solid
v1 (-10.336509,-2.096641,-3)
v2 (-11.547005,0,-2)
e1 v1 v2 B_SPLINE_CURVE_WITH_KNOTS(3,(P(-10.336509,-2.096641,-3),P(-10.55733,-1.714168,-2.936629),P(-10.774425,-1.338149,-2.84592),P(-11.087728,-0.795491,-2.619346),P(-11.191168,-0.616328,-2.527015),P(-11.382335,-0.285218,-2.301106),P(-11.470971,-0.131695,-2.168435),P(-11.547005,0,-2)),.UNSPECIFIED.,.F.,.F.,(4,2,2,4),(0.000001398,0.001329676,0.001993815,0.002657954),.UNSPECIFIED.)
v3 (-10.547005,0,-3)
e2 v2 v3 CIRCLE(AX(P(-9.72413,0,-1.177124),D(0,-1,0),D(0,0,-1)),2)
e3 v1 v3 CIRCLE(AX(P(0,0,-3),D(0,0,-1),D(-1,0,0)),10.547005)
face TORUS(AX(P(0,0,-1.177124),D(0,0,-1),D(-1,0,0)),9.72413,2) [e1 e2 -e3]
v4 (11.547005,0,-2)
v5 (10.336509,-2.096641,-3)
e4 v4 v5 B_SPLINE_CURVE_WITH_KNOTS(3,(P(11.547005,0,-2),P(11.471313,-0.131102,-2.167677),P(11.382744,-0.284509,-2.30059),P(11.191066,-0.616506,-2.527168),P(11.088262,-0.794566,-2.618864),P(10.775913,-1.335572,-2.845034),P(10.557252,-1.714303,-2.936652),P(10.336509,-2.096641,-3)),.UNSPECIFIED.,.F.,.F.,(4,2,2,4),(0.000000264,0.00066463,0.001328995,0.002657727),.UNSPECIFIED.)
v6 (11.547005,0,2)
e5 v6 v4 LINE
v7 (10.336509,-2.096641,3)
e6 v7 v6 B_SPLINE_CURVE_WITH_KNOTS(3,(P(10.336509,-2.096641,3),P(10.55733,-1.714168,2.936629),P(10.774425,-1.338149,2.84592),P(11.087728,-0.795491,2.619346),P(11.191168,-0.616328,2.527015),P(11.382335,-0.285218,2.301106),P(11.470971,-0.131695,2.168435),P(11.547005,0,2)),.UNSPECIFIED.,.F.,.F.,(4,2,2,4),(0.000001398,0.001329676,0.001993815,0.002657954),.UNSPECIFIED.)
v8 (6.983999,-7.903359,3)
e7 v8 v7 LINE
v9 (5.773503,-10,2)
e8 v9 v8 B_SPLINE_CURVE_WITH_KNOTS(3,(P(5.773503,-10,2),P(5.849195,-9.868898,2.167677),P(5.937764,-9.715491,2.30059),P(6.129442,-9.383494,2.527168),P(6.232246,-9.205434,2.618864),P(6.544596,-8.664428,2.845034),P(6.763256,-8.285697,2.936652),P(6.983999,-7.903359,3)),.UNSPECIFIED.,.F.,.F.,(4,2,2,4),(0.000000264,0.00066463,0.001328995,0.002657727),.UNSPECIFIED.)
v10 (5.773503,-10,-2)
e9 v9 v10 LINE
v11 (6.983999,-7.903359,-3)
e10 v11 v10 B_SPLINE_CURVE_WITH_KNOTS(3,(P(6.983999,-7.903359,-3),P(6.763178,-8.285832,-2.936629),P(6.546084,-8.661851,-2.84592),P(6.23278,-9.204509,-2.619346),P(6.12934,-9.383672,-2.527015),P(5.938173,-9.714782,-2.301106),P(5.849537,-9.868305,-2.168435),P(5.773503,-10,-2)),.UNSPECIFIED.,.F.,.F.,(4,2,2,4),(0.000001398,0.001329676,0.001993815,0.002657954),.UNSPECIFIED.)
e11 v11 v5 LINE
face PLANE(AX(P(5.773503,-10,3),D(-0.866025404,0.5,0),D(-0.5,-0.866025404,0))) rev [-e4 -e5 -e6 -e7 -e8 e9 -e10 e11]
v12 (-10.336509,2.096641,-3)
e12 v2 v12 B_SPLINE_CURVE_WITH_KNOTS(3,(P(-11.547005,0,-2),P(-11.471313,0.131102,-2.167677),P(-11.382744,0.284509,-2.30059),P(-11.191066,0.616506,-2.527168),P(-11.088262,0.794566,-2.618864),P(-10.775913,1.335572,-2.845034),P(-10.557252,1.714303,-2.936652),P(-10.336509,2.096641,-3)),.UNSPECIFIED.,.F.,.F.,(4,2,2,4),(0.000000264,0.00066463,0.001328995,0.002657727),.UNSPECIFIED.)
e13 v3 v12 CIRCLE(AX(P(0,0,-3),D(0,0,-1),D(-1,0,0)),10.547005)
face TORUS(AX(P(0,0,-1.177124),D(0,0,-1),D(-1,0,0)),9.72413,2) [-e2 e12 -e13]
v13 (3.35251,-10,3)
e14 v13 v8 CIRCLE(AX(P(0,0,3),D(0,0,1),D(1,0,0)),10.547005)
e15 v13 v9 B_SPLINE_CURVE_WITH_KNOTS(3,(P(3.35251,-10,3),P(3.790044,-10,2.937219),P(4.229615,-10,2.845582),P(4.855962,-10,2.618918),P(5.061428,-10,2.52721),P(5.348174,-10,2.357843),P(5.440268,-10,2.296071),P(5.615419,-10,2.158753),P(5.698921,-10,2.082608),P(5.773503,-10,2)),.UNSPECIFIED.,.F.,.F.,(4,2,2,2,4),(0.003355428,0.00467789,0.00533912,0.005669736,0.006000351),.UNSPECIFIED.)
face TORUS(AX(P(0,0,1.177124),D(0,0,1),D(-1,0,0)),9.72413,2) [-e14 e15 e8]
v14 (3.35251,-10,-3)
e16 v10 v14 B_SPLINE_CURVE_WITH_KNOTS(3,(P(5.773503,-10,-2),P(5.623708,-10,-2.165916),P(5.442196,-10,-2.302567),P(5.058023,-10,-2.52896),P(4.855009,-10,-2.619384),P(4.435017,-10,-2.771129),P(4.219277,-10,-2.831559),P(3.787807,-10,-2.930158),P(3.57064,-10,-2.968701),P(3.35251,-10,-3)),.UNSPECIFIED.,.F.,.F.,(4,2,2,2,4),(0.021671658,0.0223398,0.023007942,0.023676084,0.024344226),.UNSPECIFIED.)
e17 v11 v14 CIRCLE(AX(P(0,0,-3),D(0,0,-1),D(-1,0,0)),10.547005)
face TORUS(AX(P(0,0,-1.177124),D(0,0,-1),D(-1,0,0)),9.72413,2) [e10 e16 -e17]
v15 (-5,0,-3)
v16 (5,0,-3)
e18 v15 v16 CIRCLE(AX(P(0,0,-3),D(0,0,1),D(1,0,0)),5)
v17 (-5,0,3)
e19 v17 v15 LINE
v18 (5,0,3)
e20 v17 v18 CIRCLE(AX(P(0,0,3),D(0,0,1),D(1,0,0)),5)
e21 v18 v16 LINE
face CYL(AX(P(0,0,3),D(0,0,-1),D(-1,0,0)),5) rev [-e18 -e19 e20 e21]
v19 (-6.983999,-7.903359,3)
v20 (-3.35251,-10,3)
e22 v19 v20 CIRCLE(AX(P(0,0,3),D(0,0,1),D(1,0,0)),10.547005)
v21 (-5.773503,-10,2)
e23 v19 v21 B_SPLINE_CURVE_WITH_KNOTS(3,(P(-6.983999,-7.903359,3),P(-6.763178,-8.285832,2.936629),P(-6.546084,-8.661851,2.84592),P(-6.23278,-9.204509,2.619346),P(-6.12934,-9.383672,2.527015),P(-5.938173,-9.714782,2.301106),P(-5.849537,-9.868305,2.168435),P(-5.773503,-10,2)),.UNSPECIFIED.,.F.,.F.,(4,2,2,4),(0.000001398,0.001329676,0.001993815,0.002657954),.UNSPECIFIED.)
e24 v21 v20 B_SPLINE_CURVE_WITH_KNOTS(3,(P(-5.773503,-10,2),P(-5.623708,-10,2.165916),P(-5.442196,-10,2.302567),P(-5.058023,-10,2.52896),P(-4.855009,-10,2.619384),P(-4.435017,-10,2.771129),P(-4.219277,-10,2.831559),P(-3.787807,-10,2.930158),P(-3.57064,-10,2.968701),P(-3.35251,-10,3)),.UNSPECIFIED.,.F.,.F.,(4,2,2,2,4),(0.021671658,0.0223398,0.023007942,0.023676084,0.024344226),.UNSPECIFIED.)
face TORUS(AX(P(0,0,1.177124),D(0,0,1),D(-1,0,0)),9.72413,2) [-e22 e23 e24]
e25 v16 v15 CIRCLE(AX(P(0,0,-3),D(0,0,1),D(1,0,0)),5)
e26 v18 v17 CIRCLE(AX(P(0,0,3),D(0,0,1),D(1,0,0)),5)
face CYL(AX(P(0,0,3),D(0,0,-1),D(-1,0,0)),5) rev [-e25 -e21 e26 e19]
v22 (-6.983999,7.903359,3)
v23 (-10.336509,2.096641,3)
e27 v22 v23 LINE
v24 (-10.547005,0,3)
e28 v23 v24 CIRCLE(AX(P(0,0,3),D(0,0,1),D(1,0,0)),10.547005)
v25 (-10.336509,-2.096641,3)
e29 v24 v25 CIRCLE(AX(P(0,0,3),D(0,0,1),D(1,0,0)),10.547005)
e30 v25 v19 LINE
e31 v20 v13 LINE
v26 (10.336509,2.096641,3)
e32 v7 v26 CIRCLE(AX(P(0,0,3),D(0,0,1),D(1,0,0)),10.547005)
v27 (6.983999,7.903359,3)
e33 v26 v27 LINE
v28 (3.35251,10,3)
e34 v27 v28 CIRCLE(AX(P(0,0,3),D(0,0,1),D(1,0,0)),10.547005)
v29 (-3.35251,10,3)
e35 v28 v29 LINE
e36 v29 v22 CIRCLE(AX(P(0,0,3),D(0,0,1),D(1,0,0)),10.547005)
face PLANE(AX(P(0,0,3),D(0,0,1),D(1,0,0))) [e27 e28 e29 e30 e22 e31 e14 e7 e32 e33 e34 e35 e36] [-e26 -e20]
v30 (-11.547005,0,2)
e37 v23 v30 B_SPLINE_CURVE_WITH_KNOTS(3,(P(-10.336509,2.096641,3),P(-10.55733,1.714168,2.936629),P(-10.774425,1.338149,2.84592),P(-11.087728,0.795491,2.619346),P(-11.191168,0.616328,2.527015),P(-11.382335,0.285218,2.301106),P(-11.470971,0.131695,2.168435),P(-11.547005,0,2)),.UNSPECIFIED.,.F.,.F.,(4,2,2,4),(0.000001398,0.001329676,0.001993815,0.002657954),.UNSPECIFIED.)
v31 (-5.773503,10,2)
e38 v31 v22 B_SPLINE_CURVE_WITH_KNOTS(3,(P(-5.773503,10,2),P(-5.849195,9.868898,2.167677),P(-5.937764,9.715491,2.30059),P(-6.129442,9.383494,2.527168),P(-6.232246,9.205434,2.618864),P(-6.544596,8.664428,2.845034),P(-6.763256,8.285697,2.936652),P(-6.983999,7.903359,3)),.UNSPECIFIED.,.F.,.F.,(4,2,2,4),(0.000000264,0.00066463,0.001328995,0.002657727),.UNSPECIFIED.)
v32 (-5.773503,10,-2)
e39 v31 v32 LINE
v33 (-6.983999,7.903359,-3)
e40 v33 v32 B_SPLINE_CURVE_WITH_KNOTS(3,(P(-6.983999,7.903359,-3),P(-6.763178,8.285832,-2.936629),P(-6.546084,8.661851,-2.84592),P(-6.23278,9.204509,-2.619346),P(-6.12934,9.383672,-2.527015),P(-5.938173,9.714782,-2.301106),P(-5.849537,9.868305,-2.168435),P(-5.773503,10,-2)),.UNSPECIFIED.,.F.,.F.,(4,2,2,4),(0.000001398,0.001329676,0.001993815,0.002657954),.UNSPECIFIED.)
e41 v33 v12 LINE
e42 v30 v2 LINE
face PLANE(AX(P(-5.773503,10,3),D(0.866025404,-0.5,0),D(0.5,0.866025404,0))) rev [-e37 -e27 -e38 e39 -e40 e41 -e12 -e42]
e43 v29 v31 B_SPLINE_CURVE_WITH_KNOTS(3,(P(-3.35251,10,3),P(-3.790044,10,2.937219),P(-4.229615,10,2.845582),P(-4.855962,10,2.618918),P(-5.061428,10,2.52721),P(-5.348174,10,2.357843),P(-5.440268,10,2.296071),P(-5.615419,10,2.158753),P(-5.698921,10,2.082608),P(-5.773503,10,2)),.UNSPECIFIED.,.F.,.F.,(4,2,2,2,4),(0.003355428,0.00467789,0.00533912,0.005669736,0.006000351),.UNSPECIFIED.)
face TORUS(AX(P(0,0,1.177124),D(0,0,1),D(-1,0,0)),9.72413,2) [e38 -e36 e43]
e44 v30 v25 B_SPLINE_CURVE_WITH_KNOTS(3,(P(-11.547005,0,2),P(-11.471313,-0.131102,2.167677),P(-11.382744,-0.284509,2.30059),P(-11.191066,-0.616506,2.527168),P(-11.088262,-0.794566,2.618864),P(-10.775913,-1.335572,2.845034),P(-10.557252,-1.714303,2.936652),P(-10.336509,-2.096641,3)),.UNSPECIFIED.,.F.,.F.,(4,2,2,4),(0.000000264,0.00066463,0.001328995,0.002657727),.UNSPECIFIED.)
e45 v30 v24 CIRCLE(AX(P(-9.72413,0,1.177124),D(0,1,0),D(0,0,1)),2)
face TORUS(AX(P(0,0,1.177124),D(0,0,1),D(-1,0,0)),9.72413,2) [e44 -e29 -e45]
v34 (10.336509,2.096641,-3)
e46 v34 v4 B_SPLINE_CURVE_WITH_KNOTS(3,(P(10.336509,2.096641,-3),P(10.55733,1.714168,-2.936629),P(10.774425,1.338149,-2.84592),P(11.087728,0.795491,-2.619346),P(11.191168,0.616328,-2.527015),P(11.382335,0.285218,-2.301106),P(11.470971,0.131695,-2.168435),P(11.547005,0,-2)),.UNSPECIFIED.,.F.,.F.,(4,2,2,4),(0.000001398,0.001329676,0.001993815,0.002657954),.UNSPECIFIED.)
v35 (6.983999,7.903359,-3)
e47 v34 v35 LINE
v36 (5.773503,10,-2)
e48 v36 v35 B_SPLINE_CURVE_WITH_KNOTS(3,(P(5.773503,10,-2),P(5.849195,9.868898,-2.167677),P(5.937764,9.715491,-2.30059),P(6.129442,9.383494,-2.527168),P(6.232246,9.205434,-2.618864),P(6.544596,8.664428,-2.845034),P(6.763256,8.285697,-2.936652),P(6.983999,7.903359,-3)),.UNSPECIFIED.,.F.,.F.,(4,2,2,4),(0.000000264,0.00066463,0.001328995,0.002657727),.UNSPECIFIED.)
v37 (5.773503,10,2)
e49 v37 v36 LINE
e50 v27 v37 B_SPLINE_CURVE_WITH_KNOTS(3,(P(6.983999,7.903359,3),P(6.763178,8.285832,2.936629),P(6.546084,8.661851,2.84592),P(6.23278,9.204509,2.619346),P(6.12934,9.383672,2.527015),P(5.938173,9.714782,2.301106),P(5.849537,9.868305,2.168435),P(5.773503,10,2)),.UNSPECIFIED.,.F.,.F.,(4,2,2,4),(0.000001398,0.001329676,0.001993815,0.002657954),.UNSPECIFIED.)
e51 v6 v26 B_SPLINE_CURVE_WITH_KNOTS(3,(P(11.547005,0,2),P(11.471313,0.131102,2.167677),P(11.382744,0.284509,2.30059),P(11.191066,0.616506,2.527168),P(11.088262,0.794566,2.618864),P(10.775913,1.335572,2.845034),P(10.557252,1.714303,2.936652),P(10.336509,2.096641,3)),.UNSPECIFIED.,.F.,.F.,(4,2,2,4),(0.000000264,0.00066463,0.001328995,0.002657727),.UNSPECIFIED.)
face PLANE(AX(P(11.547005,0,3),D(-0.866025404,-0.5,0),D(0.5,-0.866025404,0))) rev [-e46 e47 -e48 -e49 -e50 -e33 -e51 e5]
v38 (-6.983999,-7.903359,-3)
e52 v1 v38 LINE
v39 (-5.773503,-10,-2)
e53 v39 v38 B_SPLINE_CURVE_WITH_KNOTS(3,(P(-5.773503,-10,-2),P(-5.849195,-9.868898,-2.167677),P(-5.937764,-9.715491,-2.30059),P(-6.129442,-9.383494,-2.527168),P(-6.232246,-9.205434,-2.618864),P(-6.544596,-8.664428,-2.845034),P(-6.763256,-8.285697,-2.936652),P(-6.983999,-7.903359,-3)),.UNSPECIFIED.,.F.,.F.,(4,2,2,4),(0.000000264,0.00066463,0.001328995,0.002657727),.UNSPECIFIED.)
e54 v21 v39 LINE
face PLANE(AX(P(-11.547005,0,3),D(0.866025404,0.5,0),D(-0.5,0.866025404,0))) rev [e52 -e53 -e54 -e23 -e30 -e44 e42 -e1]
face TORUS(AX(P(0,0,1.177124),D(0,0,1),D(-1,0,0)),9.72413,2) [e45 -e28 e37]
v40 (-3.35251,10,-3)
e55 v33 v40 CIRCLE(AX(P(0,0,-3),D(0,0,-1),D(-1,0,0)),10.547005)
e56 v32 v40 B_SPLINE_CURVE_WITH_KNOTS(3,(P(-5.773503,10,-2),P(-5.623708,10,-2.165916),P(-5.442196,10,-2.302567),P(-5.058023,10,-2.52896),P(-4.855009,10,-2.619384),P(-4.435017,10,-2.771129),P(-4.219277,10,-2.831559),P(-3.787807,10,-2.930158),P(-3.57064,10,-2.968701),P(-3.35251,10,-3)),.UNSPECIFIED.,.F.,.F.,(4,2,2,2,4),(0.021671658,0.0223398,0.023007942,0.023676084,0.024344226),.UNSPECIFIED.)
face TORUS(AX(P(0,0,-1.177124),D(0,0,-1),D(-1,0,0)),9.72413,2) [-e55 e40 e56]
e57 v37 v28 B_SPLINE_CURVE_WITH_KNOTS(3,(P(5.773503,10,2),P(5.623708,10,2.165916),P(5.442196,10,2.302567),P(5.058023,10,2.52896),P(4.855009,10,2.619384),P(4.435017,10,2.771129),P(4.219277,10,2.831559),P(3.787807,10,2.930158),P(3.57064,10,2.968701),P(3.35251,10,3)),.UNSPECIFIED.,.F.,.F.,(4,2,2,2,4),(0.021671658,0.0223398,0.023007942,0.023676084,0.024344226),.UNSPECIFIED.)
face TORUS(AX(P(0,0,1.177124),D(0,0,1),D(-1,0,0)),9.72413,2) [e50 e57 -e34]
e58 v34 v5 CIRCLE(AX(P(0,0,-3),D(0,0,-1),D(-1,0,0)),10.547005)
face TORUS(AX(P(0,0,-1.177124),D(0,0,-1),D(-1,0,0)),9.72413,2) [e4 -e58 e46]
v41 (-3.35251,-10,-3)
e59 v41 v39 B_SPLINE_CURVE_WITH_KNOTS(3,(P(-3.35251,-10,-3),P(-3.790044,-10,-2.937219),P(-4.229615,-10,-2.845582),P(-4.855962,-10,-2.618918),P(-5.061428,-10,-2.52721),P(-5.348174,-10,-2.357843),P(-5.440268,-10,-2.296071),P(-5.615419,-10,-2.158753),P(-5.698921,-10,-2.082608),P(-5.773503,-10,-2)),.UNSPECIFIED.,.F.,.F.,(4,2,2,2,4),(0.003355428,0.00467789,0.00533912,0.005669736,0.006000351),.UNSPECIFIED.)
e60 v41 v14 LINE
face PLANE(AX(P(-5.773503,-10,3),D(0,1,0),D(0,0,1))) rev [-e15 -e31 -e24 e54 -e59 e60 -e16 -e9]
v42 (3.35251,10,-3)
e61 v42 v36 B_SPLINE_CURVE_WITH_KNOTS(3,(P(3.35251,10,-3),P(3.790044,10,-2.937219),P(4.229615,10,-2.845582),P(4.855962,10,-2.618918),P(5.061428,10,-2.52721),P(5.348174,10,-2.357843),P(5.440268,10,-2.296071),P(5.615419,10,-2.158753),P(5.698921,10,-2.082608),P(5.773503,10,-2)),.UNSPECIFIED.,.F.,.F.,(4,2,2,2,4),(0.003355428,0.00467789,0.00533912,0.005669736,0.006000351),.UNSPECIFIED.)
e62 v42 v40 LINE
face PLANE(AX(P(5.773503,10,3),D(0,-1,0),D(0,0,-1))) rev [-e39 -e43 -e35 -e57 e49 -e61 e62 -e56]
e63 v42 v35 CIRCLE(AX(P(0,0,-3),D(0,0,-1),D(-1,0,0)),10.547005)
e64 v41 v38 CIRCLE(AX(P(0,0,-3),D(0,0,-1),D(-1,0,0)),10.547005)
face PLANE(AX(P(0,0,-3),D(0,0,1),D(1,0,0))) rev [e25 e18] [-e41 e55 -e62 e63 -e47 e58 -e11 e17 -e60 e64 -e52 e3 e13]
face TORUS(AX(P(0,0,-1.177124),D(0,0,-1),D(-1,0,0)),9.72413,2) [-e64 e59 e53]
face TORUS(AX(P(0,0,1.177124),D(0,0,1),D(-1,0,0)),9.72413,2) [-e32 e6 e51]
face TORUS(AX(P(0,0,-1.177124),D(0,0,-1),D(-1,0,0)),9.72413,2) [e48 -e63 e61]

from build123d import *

# Parameters (mm, degrees)
HEX_PROFILE_20AF_R     = 5
HEX_NUT_BODY_6MM_DEPTH = 3


with BuildPart() as part:
    # Hex Profile 20AF → Hex Nut Body 6mm (new, symmetric)
    with BuildSketch(Plane.XY):
        Polygon((11.547005384, 0), (5.773502692, 10), (-5.773502692, 10), (-11.547005384, 0), (-5.773502692, -10), (5.773502692, -10), align=None)
        Circle(HEX_PROFILE_20AF_R, mode=Mode.SUBTRACT)
    extrude(amount=HEX_NUT_BODY_6MM_DEPTH, both=True)

    # Edge Chamfer Profile → Edge Chamfer Cut (revolve, cut)
    with BuildSketch(Plane(origin=(0, 0, 0), x_dir=(1, 0, 0), z_dir=(0, 1, 0))):
        with BuildLine():
            Line((10.547005384, 3), (11.547005384, 3))
            Line((11.547005384, 3), (11.547005384, 2))
            ThreePointArc((11.547005384, 2), (11.138343291, 2.591337907), (10.547005384, 3))
        make_face()
    edge_chamfer_cut = revolve(axis=Axis((0, 0, -5.076869621), (0, 0, 1)), mode=Mode.SUBTRACT)

    # Edge Chamfer Mirror: Edge Chamfer Cut across plane
    add(edge_chamfer_cut.mirror(Plane.XY), mode=Mode.SUBTRACT)


solid = part.part
